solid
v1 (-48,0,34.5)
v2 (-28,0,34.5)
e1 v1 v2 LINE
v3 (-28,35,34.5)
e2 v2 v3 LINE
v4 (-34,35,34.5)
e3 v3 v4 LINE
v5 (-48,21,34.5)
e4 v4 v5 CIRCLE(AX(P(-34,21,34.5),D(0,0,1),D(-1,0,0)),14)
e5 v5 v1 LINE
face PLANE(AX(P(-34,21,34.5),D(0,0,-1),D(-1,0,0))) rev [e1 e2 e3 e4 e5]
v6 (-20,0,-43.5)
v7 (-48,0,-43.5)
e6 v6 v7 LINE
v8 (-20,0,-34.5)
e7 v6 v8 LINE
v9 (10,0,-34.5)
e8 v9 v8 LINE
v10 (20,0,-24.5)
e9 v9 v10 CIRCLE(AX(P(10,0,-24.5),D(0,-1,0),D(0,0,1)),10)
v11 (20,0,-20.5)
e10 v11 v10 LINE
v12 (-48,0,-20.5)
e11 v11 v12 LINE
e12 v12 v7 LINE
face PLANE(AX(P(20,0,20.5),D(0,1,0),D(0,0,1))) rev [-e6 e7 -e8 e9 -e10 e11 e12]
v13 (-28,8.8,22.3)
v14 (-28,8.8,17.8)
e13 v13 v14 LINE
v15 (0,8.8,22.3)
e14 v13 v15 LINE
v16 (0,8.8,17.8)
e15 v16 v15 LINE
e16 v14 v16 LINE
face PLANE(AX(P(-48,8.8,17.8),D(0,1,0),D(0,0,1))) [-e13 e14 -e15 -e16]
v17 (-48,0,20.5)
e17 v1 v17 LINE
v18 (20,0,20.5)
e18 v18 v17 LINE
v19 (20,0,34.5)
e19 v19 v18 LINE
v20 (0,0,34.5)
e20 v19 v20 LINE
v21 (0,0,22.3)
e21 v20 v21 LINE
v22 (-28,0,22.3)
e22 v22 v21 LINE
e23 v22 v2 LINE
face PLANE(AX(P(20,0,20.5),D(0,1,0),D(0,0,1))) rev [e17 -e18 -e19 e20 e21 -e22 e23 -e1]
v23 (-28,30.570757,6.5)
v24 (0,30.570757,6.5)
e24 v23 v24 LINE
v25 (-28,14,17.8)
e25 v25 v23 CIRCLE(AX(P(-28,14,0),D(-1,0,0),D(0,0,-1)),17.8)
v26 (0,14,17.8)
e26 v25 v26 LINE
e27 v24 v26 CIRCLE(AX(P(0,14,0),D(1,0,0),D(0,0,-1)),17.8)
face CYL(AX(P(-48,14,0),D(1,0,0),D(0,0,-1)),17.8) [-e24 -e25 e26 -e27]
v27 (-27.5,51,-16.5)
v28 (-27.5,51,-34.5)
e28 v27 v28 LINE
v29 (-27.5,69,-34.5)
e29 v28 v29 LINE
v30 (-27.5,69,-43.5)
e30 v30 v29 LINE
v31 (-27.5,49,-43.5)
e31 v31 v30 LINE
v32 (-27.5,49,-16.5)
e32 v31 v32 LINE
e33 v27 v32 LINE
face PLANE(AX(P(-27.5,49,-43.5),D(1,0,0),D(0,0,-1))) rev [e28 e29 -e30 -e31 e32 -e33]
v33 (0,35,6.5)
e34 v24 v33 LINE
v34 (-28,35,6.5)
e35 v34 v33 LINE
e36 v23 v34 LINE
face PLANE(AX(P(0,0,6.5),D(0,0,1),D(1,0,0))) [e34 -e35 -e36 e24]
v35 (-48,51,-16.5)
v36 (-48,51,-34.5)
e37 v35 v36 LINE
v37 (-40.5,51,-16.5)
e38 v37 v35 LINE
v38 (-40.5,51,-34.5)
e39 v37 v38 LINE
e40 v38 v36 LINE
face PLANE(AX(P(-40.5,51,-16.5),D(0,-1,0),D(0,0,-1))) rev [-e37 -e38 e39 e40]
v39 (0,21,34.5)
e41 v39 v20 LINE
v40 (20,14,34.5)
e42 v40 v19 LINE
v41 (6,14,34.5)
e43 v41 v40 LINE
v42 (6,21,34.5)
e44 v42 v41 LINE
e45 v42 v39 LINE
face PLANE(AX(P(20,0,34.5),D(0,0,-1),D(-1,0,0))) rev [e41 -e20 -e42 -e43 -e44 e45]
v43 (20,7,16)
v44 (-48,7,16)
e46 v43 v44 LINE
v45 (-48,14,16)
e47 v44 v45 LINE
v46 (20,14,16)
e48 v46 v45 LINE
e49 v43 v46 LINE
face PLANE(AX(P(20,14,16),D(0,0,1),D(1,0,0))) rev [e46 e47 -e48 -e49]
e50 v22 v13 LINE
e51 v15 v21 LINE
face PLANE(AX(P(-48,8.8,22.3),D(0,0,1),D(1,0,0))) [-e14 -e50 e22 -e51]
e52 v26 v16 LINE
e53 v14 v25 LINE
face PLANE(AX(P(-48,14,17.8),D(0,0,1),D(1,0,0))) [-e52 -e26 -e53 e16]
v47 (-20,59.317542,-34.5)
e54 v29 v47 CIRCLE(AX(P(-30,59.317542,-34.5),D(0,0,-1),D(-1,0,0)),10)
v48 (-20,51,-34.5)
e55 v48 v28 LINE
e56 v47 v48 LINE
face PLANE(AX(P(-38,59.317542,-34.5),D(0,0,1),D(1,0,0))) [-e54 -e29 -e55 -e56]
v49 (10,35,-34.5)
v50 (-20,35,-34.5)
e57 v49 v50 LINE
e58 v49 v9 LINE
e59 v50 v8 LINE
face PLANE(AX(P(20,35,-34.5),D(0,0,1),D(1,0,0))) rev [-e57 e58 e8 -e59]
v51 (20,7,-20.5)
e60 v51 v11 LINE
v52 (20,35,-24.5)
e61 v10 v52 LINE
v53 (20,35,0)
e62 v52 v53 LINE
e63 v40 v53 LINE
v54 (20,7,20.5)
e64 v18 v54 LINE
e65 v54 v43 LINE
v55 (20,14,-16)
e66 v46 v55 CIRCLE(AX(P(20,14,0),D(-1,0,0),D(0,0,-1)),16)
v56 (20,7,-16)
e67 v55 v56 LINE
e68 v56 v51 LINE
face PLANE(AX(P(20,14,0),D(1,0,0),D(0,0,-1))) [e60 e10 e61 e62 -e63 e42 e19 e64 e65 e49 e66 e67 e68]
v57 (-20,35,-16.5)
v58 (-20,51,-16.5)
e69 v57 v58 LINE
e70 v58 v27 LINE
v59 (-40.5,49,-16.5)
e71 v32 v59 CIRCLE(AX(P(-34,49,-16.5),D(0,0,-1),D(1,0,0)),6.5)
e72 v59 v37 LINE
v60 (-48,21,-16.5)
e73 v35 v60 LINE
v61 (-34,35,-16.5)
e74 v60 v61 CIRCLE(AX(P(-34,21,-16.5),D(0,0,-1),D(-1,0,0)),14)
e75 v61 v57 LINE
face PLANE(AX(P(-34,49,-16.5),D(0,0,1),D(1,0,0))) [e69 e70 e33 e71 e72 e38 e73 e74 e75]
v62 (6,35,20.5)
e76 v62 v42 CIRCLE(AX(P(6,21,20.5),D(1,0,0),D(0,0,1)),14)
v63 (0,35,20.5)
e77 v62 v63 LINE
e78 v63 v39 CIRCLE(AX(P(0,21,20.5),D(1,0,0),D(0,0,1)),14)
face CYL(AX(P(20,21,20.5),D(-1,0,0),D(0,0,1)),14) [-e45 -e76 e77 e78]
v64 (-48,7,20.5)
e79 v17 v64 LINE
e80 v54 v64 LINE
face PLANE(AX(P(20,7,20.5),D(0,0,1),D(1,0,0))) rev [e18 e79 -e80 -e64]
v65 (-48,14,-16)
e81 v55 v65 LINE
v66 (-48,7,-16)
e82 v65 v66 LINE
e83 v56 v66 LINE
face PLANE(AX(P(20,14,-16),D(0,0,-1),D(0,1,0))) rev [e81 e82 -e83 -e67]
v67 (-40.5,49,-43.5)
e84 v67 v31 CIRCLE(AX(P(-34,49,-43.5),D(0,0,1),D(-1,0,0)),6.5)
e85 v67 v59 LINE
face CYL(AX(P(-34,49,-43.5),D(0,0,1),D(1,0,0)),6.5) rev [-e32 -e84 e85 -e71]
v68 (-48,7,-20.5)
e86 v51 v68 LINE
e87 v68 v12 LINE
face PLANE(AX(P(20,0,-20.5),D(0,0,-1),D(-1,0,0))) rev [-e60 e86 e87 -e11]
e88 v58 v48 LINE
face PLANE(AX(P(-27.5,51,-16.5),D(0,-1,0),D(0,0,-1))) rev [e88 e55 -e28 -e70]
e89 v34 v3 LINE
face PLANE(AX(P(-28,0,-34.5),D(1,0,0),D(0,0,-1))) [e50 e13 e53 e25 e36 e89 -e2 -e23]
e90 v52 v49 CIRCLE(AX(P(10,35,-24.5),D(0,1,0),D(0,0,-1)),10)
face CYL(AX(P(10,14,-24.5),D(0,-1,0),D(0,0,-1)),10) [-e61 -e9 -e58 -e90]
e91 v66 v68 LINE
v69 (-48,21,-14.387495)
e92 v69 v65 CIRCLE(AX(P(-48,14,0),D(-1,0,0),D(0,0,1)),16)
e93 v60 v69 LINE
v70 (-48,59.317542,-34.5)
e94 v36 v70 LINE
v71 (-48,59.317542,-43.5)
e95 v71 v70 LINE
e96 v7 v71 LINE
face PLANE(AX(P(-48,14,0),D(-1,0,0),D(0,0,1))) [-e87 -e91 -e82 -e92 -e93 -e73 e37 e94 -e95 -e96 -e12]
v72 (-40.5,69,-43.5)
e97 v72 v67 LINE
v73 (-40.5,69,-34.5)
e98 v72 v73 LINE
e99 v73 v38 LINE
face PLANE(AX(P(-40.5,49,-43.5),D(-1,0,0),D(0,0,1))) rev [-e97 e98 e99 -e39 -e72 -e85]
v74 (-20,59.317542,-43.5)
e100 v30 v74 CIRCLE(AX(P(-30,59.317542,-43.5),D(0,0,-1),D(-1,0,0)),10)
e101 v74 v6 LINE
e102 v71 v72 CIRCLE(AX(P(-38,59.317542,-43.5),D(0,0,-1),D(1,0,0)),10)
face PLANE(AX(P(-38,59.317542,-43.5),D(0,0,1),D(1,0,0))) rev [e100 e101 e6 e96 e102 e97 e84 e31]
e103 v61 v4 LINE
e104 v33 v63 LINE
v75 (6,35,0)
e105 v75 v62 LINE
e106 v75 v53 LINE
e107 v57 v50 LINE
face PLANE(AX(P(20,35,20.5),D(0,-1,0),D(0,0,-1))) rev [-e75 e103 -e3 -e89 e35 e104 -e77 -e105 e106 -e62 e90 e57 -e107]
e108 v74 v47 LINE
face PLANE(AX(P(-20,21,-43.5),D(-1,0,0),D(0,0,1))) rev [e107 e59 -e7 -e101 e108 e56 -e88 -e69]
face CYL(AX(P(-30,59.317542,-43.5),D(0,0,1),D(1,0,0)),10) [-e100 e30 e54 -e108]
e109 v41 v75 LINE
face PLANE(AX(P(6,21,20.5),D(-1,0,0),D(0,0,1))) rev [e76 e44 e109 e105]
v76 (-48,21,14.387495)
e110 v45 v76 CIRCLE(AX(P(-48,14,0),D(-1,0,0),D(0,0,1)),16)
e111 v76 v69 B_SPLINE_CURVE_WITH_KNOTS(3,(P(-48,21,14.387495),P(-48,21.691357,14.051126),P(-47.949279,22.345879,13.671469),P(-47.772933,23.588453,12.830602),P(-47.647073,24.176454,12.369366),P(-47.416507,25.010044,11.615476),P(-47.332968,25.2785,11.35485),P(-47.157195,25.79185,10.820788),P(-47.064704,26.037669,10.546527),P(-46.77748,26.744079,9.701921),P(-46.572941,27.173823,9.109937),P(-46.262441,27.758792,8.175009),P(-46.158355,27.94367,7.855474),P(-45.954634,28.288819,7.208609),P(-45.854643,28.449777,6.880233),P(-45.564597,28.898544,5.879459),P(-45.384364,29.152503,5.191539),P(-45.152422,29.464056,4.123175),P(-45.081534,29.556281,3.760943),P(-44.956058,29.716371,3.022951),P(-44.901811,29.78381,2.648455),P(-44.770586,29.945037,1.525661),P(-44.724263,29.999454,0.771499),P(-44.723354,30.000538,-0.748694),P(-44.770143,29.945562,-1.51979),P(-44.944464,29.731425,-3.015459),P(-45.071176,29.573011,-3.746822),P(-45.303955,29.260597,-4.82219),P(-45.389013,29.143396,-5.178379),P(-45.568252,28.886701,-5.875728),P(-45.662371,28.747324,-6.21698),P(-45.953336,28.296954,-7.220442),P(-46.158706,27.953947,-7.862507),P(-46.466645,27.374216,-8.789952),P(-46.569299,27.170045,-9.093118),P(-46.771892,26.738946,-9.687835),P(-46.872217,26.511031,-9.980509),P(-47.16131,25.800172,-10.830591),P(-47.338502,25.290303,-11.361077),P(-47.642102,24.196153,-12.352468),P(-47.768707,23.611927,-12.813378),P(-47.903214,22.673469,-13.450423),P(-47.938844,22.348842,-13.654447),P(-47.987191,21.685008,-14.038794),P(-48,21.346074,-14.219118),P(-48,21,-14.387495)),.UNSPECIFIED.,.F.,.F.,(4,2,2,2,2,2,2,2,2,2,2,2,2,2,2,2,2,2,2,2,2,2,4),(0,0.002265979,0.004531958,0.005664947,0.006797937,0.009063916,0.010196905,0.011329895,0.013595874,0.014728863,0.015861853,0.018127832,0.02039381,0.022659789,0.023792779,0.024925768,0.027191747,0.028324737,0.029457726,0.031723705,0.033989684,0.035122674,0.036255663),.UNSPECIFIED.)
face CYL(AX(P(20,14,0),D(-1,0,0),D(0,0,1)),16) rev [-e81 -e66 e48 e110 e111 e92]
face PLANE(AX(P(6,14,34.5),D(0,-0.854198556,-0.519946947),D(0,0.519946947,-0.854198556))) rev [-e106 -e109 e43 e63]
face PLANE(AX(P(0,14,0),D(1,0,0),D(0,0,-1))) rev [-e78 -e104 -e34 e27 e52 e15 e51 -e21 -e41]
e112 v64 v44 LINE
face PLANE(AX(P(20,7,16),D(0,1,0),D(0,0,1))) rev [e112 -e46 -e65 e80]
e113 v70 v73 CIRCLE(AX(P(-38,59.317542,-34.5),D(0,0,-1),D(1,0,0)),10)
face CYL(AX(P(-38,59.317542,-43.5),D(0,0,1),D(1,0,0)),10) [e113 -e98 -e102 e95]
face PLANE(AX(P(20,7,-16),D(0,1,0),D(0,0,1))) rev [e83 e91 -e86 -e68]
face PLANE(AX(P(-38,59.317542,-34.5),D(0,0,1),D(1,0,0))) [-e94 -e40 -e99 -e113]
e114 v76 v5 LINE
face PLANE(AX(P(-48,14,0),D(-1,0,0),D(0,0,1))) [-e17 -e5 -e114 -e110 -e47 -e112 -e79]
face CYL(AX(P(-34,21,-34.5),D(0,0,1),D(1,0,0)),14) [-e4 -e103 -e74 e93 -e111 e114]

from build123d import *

# Parameters (mm, degrees)
BASE_BODY_20MM_DEPTH       = 20
BASE_START                 = -14
BASE_SLOT_CUT_DEPTH        = 14
THIN_START                 = -68
THIN_WALL_BOSS_1_8MM_DEPTH = 68
JOURNAL_BLOCK_BOSS_DEPTH   = 69
JOURNAL_START              = -69
JOURNAL_BORE_CUT_DEPTH     = 69
JOURNAL_RELIEF_CUT_DEPTH   = 69
CROSS_ARM_BOSS_DEPTH       = 9
UPRIGHT_LUG_SKETCH_W       = 28
UPRIGHT_LUG_SKETCH_H       = 41
UPRIGHT_LUG_BOSS_DEPTH     = 35
LUG_START                  = -69
LUG_SLOT_CUT_DEPTH         = 69
SIDE_START                 = 18
SIDE_RIB_BOSS_DEPTH        = 18
BASE_EDGE_FILLET_R10_R     = 10


with BuildPart() as part:
    # Base Profile Sketch → Base Body 20mm (new body)
    with BuildSketch(Plane(origin=(0, 0, 0), x_dir=(0, 0, -1), z_dir=(1, 0, 0))):
        with BuildLine():
            Line((20.5, 0), (20.5, 7))
            Line((20.5, 7), (16, 7))
            Line((16, 7), (16, 14))
            ThreePointArc((16, 14), (0, 30), (-16, 14))
            Line((-16, 14), (-16, 7))
            Line((-16, 7), (-20.5, 7))
            Line((-20.5, 7), (-20.5, 0))
            Line((-20.5, 0), (-34.5, 0))
            Line((-34.5, 0), (-34.5, 21))
            ThreePointArc((-34.5, 21), (-30.399494937, 30.899494937), (-20.5, 35))
            Line((-20.5, 35), (34.5, 35))
            Line((34.5, 35), (34.5, 0))
            Line((34.5, 0), (20.5, 0))
        make_face()
    extrude(amount=BASE_BODY_20MM_DEPTH)

    # Base Slot Sketch → Base Slot Cut (cut)
    with BuildSketch(Plane(origin=(20, 0, 0), x_dir=(0, 0, -1), z_dir=(1, 0, 0)).offset(BASE_START)):
        with BuildLine():
            Line((-34.5, 14), (0, 35))
            Line((0, 35), (-20.5, 35))
            ThreePointArc((-20.5, 35), (-30.399494937, 30.899494937), (-34.5, 21))
            Line((-34.5, 21), (-34.5, 14))
        make_face()
    extrude(amount=BASE_SLOT_CUT_DEPTH, mode=Mode.SUBTRACT)

    # Thin Wall Profile Sketch → Thin Wall Boss 1.8mm (add)
    with BuildSketch(Plane(origin=(20, 0, 0), x_dir=(0, 0, -1), z_dir=(1, 0, 0)).offset(THIN_START)):
        with BuildLine():
            Line((-16, 14), (-16, 7))
            Line((-16, 7), (-20.5, 7))
            Line((-20.5, 7), (-20.5, 0))
            Line((-20.5, 0), (-22.3, 0))
            Line((-22.3, 0), (-22.3, 8.8))
            Line((-22.3, 8.8), (-17.8, 8.8))
            Line((-17.8, 8.8), (-17.8, 14))
            ThreePointArc((-17.8, 14), (0, 31.8), (17.8, 14))
            Line((17.8, 14), (17.8, 8.8))
            Line((17.8, 8.8), (22.3, 8.8))
            Line((22.3, 8.8), (22.3, 0))
            Line((22.3, 0), (20.5, 0))
            Line((20.5, 0), (20.5, 7))
            Line((20.5, 7), (16, 7))
            Line((16, 7), (16, 14))
            ThreePointArc((16, 14), (0, 30), (-16, 14))
        make_face()
    extrude(amount=THIN_WALL_BOSS_1_8MM_DEPTH)

    # Journal Block Sketch → Journal Block Boss (add)
    with BuildSketch(Plane.XY.offset(34.5)):
        with BuildLine():
            Line((-48, 0), (-28, 0))
            Line((-28, 0), (-28, 35))
            Line((-28, 35), (-34, 35))
            ThreePointArc((-34, 35), (-43.899494937, 30.899494937), (-48, 21))
            Line((-48, 21), (-48, 0))
        make_face()
    extrude(amount=-JOURNAL_BLOCK_BOSS_DEPTH)

    # Journal Bore Sketch → Journal Bore Cut (cut)
    with BuildSketch(Plane(origin=(20, 0, 0), x_dir=(0, 0, -1), z_dir=(1, 0, 0)).offset(JOURNAL_START)):
        with BuildLine():
            Line((-16, 14), (-16, 7))
            Line((-16, 7), (-20.5, 7))
            Line((-20.5, 7), (-20.5, 0))
            Line((-20.5, 0), (20.5, 0))
            Line((20.5, 0), (20.5, 7))
            Line((20.5, 7), (16, 7))
            Line((16, 7), (16, 14))
            ThreePointArc((16, 14), (0, 30), (-16, 14))
        make_face()
    extrude(amount=JOURNAL_BORE_CUT_DEPTH, mode=Mode.SUBTRACT)

    # Journal Relief Sketch → Journal Relief Cut (cut)
    with BuildSketch(Plane.XY.offset(34.5)):
        with BuildLine():
            Line((-48, 21), (-48, 35))
            Line((-48, 35), (-34, 35))
            ThreePointArc((-34, 35), (-43.899494937, 30.899494937), (-48, 21))
        make_face()
    extrude(amount=-JOURNAL_RELIEF_CUT_DEPTH, mode=Mode.SUBTRACT)

    # Cross Arm Sketch → Cross Arm Boss (add)
    with BuildSketch(Plane(origin=(0, 0, -34.5), x_dir=(-1, 0, 0), z_dir=(0, 0, -1))):
        with BuildLine():
            Line((48, 21), (48, 35))
            Line((48, 35), (48, 59))
            Line((48, 59), (48, 59.317541634))
            ThreePointArc((48, 59.317541634), (45.90569415, 65.441265991), (40.5, 69))
            Line((40.5, 69), (40.5, 49))
            ThreePointArc((40.5, 49), (34, 42.5), (27.5, 49))
            Line((27.5, 49), (27.5, 69))
            ThreePointArc((27.5, 69), (22.09430585, 65.441265991), (20, 59.317541634))
            Line((20, 59.317541634), (20, 21))
            Line((20, 21), (20, 0))
            Line((20, 0), (48, 0))
            Line((48, 0), (48, 21))
        make_face()
    extrude(amount=CROSS_ARM_BOSS_DEPTH)

    # Upright Lug Sketch → Upright Lug Boss (add)
    with BuildSketch(Plane(origin=(0, 35, 0), x_dir=(1, 0, 0), z_dir=(0, 1, 0))):
        with Locations((-14, 14)):
            Rectangle(UPRIGHT_LUG_SKETCH_W, UPRIGHT_LUG_SKETCH_H)
    extrude(amount=-UPRIGHT_LUG_BOSS_DEPTH)

    # Lug Slot Sketch → Lug Slot Cut (cut)
    with BuildSketch(Plane(origin=(20, 0, 0), x_dir=(0, 0, -1), z_dir=(1, 0, 0)).offset(LUG_START)):
        with BuildLine():
            Line((-16, 14), (-16, 7))
            Line((-16, 7), (-20.5, 7))
            Line((-20.5, 7), (-20.5, 0))
            Line((-20.5, 0), (20.5, 0))
            Line((20.5, 0), (20.5, 7))
            Line((20.5, 7), (16, 7))
            Line((16, 7), (16, 14))
            ThreePointArc((16, 14), (0, 30), (-16, 14))
        make_face()
    extrude(amount=LUG_SLOT_CUT_DEPTH, mode=Mode.SUBTRACT)

    # Side Rib Sketch → Side Rib Boss (add)
    with BuildSketch(Plane.XY.offset(-34.5).offset(SIDE_START)):
        with BuildLine():
            Line((-20, 35), (-20, 51))
            Line((-20, 51), (-27.5, 51))
            Line((-27.5, 51), (-27.5, 49))
            ThreePointArc((-27.5, 49), (-34, 42.5), (-40.5, 49))
            Line((-40.5, 49), (-40.5, 51))
            Line((-40.5, 51), (-48, 51))
            Line((-48, 51), (-48, 21))
            ThreePointArc((-48, 21), (-43.899494937, 30.899494937), (-34, 35))
            Line((-34, 35), (-20, 35))
        make_face()
    extrude(amount=-SIDE_RIB_BOSS_DEPTH)

    # Base Edge Fillet R10
    base_edge_fillet_r10_edges = [part.edges().sort_by_distance(p)[0] for p in [
        (20, 17.5, -34.5),
    ]]
    fillet(base_edge_fillet_r10_edges, radius=BASE_EDGE_FILLET_R10_R)


solid = part.part
